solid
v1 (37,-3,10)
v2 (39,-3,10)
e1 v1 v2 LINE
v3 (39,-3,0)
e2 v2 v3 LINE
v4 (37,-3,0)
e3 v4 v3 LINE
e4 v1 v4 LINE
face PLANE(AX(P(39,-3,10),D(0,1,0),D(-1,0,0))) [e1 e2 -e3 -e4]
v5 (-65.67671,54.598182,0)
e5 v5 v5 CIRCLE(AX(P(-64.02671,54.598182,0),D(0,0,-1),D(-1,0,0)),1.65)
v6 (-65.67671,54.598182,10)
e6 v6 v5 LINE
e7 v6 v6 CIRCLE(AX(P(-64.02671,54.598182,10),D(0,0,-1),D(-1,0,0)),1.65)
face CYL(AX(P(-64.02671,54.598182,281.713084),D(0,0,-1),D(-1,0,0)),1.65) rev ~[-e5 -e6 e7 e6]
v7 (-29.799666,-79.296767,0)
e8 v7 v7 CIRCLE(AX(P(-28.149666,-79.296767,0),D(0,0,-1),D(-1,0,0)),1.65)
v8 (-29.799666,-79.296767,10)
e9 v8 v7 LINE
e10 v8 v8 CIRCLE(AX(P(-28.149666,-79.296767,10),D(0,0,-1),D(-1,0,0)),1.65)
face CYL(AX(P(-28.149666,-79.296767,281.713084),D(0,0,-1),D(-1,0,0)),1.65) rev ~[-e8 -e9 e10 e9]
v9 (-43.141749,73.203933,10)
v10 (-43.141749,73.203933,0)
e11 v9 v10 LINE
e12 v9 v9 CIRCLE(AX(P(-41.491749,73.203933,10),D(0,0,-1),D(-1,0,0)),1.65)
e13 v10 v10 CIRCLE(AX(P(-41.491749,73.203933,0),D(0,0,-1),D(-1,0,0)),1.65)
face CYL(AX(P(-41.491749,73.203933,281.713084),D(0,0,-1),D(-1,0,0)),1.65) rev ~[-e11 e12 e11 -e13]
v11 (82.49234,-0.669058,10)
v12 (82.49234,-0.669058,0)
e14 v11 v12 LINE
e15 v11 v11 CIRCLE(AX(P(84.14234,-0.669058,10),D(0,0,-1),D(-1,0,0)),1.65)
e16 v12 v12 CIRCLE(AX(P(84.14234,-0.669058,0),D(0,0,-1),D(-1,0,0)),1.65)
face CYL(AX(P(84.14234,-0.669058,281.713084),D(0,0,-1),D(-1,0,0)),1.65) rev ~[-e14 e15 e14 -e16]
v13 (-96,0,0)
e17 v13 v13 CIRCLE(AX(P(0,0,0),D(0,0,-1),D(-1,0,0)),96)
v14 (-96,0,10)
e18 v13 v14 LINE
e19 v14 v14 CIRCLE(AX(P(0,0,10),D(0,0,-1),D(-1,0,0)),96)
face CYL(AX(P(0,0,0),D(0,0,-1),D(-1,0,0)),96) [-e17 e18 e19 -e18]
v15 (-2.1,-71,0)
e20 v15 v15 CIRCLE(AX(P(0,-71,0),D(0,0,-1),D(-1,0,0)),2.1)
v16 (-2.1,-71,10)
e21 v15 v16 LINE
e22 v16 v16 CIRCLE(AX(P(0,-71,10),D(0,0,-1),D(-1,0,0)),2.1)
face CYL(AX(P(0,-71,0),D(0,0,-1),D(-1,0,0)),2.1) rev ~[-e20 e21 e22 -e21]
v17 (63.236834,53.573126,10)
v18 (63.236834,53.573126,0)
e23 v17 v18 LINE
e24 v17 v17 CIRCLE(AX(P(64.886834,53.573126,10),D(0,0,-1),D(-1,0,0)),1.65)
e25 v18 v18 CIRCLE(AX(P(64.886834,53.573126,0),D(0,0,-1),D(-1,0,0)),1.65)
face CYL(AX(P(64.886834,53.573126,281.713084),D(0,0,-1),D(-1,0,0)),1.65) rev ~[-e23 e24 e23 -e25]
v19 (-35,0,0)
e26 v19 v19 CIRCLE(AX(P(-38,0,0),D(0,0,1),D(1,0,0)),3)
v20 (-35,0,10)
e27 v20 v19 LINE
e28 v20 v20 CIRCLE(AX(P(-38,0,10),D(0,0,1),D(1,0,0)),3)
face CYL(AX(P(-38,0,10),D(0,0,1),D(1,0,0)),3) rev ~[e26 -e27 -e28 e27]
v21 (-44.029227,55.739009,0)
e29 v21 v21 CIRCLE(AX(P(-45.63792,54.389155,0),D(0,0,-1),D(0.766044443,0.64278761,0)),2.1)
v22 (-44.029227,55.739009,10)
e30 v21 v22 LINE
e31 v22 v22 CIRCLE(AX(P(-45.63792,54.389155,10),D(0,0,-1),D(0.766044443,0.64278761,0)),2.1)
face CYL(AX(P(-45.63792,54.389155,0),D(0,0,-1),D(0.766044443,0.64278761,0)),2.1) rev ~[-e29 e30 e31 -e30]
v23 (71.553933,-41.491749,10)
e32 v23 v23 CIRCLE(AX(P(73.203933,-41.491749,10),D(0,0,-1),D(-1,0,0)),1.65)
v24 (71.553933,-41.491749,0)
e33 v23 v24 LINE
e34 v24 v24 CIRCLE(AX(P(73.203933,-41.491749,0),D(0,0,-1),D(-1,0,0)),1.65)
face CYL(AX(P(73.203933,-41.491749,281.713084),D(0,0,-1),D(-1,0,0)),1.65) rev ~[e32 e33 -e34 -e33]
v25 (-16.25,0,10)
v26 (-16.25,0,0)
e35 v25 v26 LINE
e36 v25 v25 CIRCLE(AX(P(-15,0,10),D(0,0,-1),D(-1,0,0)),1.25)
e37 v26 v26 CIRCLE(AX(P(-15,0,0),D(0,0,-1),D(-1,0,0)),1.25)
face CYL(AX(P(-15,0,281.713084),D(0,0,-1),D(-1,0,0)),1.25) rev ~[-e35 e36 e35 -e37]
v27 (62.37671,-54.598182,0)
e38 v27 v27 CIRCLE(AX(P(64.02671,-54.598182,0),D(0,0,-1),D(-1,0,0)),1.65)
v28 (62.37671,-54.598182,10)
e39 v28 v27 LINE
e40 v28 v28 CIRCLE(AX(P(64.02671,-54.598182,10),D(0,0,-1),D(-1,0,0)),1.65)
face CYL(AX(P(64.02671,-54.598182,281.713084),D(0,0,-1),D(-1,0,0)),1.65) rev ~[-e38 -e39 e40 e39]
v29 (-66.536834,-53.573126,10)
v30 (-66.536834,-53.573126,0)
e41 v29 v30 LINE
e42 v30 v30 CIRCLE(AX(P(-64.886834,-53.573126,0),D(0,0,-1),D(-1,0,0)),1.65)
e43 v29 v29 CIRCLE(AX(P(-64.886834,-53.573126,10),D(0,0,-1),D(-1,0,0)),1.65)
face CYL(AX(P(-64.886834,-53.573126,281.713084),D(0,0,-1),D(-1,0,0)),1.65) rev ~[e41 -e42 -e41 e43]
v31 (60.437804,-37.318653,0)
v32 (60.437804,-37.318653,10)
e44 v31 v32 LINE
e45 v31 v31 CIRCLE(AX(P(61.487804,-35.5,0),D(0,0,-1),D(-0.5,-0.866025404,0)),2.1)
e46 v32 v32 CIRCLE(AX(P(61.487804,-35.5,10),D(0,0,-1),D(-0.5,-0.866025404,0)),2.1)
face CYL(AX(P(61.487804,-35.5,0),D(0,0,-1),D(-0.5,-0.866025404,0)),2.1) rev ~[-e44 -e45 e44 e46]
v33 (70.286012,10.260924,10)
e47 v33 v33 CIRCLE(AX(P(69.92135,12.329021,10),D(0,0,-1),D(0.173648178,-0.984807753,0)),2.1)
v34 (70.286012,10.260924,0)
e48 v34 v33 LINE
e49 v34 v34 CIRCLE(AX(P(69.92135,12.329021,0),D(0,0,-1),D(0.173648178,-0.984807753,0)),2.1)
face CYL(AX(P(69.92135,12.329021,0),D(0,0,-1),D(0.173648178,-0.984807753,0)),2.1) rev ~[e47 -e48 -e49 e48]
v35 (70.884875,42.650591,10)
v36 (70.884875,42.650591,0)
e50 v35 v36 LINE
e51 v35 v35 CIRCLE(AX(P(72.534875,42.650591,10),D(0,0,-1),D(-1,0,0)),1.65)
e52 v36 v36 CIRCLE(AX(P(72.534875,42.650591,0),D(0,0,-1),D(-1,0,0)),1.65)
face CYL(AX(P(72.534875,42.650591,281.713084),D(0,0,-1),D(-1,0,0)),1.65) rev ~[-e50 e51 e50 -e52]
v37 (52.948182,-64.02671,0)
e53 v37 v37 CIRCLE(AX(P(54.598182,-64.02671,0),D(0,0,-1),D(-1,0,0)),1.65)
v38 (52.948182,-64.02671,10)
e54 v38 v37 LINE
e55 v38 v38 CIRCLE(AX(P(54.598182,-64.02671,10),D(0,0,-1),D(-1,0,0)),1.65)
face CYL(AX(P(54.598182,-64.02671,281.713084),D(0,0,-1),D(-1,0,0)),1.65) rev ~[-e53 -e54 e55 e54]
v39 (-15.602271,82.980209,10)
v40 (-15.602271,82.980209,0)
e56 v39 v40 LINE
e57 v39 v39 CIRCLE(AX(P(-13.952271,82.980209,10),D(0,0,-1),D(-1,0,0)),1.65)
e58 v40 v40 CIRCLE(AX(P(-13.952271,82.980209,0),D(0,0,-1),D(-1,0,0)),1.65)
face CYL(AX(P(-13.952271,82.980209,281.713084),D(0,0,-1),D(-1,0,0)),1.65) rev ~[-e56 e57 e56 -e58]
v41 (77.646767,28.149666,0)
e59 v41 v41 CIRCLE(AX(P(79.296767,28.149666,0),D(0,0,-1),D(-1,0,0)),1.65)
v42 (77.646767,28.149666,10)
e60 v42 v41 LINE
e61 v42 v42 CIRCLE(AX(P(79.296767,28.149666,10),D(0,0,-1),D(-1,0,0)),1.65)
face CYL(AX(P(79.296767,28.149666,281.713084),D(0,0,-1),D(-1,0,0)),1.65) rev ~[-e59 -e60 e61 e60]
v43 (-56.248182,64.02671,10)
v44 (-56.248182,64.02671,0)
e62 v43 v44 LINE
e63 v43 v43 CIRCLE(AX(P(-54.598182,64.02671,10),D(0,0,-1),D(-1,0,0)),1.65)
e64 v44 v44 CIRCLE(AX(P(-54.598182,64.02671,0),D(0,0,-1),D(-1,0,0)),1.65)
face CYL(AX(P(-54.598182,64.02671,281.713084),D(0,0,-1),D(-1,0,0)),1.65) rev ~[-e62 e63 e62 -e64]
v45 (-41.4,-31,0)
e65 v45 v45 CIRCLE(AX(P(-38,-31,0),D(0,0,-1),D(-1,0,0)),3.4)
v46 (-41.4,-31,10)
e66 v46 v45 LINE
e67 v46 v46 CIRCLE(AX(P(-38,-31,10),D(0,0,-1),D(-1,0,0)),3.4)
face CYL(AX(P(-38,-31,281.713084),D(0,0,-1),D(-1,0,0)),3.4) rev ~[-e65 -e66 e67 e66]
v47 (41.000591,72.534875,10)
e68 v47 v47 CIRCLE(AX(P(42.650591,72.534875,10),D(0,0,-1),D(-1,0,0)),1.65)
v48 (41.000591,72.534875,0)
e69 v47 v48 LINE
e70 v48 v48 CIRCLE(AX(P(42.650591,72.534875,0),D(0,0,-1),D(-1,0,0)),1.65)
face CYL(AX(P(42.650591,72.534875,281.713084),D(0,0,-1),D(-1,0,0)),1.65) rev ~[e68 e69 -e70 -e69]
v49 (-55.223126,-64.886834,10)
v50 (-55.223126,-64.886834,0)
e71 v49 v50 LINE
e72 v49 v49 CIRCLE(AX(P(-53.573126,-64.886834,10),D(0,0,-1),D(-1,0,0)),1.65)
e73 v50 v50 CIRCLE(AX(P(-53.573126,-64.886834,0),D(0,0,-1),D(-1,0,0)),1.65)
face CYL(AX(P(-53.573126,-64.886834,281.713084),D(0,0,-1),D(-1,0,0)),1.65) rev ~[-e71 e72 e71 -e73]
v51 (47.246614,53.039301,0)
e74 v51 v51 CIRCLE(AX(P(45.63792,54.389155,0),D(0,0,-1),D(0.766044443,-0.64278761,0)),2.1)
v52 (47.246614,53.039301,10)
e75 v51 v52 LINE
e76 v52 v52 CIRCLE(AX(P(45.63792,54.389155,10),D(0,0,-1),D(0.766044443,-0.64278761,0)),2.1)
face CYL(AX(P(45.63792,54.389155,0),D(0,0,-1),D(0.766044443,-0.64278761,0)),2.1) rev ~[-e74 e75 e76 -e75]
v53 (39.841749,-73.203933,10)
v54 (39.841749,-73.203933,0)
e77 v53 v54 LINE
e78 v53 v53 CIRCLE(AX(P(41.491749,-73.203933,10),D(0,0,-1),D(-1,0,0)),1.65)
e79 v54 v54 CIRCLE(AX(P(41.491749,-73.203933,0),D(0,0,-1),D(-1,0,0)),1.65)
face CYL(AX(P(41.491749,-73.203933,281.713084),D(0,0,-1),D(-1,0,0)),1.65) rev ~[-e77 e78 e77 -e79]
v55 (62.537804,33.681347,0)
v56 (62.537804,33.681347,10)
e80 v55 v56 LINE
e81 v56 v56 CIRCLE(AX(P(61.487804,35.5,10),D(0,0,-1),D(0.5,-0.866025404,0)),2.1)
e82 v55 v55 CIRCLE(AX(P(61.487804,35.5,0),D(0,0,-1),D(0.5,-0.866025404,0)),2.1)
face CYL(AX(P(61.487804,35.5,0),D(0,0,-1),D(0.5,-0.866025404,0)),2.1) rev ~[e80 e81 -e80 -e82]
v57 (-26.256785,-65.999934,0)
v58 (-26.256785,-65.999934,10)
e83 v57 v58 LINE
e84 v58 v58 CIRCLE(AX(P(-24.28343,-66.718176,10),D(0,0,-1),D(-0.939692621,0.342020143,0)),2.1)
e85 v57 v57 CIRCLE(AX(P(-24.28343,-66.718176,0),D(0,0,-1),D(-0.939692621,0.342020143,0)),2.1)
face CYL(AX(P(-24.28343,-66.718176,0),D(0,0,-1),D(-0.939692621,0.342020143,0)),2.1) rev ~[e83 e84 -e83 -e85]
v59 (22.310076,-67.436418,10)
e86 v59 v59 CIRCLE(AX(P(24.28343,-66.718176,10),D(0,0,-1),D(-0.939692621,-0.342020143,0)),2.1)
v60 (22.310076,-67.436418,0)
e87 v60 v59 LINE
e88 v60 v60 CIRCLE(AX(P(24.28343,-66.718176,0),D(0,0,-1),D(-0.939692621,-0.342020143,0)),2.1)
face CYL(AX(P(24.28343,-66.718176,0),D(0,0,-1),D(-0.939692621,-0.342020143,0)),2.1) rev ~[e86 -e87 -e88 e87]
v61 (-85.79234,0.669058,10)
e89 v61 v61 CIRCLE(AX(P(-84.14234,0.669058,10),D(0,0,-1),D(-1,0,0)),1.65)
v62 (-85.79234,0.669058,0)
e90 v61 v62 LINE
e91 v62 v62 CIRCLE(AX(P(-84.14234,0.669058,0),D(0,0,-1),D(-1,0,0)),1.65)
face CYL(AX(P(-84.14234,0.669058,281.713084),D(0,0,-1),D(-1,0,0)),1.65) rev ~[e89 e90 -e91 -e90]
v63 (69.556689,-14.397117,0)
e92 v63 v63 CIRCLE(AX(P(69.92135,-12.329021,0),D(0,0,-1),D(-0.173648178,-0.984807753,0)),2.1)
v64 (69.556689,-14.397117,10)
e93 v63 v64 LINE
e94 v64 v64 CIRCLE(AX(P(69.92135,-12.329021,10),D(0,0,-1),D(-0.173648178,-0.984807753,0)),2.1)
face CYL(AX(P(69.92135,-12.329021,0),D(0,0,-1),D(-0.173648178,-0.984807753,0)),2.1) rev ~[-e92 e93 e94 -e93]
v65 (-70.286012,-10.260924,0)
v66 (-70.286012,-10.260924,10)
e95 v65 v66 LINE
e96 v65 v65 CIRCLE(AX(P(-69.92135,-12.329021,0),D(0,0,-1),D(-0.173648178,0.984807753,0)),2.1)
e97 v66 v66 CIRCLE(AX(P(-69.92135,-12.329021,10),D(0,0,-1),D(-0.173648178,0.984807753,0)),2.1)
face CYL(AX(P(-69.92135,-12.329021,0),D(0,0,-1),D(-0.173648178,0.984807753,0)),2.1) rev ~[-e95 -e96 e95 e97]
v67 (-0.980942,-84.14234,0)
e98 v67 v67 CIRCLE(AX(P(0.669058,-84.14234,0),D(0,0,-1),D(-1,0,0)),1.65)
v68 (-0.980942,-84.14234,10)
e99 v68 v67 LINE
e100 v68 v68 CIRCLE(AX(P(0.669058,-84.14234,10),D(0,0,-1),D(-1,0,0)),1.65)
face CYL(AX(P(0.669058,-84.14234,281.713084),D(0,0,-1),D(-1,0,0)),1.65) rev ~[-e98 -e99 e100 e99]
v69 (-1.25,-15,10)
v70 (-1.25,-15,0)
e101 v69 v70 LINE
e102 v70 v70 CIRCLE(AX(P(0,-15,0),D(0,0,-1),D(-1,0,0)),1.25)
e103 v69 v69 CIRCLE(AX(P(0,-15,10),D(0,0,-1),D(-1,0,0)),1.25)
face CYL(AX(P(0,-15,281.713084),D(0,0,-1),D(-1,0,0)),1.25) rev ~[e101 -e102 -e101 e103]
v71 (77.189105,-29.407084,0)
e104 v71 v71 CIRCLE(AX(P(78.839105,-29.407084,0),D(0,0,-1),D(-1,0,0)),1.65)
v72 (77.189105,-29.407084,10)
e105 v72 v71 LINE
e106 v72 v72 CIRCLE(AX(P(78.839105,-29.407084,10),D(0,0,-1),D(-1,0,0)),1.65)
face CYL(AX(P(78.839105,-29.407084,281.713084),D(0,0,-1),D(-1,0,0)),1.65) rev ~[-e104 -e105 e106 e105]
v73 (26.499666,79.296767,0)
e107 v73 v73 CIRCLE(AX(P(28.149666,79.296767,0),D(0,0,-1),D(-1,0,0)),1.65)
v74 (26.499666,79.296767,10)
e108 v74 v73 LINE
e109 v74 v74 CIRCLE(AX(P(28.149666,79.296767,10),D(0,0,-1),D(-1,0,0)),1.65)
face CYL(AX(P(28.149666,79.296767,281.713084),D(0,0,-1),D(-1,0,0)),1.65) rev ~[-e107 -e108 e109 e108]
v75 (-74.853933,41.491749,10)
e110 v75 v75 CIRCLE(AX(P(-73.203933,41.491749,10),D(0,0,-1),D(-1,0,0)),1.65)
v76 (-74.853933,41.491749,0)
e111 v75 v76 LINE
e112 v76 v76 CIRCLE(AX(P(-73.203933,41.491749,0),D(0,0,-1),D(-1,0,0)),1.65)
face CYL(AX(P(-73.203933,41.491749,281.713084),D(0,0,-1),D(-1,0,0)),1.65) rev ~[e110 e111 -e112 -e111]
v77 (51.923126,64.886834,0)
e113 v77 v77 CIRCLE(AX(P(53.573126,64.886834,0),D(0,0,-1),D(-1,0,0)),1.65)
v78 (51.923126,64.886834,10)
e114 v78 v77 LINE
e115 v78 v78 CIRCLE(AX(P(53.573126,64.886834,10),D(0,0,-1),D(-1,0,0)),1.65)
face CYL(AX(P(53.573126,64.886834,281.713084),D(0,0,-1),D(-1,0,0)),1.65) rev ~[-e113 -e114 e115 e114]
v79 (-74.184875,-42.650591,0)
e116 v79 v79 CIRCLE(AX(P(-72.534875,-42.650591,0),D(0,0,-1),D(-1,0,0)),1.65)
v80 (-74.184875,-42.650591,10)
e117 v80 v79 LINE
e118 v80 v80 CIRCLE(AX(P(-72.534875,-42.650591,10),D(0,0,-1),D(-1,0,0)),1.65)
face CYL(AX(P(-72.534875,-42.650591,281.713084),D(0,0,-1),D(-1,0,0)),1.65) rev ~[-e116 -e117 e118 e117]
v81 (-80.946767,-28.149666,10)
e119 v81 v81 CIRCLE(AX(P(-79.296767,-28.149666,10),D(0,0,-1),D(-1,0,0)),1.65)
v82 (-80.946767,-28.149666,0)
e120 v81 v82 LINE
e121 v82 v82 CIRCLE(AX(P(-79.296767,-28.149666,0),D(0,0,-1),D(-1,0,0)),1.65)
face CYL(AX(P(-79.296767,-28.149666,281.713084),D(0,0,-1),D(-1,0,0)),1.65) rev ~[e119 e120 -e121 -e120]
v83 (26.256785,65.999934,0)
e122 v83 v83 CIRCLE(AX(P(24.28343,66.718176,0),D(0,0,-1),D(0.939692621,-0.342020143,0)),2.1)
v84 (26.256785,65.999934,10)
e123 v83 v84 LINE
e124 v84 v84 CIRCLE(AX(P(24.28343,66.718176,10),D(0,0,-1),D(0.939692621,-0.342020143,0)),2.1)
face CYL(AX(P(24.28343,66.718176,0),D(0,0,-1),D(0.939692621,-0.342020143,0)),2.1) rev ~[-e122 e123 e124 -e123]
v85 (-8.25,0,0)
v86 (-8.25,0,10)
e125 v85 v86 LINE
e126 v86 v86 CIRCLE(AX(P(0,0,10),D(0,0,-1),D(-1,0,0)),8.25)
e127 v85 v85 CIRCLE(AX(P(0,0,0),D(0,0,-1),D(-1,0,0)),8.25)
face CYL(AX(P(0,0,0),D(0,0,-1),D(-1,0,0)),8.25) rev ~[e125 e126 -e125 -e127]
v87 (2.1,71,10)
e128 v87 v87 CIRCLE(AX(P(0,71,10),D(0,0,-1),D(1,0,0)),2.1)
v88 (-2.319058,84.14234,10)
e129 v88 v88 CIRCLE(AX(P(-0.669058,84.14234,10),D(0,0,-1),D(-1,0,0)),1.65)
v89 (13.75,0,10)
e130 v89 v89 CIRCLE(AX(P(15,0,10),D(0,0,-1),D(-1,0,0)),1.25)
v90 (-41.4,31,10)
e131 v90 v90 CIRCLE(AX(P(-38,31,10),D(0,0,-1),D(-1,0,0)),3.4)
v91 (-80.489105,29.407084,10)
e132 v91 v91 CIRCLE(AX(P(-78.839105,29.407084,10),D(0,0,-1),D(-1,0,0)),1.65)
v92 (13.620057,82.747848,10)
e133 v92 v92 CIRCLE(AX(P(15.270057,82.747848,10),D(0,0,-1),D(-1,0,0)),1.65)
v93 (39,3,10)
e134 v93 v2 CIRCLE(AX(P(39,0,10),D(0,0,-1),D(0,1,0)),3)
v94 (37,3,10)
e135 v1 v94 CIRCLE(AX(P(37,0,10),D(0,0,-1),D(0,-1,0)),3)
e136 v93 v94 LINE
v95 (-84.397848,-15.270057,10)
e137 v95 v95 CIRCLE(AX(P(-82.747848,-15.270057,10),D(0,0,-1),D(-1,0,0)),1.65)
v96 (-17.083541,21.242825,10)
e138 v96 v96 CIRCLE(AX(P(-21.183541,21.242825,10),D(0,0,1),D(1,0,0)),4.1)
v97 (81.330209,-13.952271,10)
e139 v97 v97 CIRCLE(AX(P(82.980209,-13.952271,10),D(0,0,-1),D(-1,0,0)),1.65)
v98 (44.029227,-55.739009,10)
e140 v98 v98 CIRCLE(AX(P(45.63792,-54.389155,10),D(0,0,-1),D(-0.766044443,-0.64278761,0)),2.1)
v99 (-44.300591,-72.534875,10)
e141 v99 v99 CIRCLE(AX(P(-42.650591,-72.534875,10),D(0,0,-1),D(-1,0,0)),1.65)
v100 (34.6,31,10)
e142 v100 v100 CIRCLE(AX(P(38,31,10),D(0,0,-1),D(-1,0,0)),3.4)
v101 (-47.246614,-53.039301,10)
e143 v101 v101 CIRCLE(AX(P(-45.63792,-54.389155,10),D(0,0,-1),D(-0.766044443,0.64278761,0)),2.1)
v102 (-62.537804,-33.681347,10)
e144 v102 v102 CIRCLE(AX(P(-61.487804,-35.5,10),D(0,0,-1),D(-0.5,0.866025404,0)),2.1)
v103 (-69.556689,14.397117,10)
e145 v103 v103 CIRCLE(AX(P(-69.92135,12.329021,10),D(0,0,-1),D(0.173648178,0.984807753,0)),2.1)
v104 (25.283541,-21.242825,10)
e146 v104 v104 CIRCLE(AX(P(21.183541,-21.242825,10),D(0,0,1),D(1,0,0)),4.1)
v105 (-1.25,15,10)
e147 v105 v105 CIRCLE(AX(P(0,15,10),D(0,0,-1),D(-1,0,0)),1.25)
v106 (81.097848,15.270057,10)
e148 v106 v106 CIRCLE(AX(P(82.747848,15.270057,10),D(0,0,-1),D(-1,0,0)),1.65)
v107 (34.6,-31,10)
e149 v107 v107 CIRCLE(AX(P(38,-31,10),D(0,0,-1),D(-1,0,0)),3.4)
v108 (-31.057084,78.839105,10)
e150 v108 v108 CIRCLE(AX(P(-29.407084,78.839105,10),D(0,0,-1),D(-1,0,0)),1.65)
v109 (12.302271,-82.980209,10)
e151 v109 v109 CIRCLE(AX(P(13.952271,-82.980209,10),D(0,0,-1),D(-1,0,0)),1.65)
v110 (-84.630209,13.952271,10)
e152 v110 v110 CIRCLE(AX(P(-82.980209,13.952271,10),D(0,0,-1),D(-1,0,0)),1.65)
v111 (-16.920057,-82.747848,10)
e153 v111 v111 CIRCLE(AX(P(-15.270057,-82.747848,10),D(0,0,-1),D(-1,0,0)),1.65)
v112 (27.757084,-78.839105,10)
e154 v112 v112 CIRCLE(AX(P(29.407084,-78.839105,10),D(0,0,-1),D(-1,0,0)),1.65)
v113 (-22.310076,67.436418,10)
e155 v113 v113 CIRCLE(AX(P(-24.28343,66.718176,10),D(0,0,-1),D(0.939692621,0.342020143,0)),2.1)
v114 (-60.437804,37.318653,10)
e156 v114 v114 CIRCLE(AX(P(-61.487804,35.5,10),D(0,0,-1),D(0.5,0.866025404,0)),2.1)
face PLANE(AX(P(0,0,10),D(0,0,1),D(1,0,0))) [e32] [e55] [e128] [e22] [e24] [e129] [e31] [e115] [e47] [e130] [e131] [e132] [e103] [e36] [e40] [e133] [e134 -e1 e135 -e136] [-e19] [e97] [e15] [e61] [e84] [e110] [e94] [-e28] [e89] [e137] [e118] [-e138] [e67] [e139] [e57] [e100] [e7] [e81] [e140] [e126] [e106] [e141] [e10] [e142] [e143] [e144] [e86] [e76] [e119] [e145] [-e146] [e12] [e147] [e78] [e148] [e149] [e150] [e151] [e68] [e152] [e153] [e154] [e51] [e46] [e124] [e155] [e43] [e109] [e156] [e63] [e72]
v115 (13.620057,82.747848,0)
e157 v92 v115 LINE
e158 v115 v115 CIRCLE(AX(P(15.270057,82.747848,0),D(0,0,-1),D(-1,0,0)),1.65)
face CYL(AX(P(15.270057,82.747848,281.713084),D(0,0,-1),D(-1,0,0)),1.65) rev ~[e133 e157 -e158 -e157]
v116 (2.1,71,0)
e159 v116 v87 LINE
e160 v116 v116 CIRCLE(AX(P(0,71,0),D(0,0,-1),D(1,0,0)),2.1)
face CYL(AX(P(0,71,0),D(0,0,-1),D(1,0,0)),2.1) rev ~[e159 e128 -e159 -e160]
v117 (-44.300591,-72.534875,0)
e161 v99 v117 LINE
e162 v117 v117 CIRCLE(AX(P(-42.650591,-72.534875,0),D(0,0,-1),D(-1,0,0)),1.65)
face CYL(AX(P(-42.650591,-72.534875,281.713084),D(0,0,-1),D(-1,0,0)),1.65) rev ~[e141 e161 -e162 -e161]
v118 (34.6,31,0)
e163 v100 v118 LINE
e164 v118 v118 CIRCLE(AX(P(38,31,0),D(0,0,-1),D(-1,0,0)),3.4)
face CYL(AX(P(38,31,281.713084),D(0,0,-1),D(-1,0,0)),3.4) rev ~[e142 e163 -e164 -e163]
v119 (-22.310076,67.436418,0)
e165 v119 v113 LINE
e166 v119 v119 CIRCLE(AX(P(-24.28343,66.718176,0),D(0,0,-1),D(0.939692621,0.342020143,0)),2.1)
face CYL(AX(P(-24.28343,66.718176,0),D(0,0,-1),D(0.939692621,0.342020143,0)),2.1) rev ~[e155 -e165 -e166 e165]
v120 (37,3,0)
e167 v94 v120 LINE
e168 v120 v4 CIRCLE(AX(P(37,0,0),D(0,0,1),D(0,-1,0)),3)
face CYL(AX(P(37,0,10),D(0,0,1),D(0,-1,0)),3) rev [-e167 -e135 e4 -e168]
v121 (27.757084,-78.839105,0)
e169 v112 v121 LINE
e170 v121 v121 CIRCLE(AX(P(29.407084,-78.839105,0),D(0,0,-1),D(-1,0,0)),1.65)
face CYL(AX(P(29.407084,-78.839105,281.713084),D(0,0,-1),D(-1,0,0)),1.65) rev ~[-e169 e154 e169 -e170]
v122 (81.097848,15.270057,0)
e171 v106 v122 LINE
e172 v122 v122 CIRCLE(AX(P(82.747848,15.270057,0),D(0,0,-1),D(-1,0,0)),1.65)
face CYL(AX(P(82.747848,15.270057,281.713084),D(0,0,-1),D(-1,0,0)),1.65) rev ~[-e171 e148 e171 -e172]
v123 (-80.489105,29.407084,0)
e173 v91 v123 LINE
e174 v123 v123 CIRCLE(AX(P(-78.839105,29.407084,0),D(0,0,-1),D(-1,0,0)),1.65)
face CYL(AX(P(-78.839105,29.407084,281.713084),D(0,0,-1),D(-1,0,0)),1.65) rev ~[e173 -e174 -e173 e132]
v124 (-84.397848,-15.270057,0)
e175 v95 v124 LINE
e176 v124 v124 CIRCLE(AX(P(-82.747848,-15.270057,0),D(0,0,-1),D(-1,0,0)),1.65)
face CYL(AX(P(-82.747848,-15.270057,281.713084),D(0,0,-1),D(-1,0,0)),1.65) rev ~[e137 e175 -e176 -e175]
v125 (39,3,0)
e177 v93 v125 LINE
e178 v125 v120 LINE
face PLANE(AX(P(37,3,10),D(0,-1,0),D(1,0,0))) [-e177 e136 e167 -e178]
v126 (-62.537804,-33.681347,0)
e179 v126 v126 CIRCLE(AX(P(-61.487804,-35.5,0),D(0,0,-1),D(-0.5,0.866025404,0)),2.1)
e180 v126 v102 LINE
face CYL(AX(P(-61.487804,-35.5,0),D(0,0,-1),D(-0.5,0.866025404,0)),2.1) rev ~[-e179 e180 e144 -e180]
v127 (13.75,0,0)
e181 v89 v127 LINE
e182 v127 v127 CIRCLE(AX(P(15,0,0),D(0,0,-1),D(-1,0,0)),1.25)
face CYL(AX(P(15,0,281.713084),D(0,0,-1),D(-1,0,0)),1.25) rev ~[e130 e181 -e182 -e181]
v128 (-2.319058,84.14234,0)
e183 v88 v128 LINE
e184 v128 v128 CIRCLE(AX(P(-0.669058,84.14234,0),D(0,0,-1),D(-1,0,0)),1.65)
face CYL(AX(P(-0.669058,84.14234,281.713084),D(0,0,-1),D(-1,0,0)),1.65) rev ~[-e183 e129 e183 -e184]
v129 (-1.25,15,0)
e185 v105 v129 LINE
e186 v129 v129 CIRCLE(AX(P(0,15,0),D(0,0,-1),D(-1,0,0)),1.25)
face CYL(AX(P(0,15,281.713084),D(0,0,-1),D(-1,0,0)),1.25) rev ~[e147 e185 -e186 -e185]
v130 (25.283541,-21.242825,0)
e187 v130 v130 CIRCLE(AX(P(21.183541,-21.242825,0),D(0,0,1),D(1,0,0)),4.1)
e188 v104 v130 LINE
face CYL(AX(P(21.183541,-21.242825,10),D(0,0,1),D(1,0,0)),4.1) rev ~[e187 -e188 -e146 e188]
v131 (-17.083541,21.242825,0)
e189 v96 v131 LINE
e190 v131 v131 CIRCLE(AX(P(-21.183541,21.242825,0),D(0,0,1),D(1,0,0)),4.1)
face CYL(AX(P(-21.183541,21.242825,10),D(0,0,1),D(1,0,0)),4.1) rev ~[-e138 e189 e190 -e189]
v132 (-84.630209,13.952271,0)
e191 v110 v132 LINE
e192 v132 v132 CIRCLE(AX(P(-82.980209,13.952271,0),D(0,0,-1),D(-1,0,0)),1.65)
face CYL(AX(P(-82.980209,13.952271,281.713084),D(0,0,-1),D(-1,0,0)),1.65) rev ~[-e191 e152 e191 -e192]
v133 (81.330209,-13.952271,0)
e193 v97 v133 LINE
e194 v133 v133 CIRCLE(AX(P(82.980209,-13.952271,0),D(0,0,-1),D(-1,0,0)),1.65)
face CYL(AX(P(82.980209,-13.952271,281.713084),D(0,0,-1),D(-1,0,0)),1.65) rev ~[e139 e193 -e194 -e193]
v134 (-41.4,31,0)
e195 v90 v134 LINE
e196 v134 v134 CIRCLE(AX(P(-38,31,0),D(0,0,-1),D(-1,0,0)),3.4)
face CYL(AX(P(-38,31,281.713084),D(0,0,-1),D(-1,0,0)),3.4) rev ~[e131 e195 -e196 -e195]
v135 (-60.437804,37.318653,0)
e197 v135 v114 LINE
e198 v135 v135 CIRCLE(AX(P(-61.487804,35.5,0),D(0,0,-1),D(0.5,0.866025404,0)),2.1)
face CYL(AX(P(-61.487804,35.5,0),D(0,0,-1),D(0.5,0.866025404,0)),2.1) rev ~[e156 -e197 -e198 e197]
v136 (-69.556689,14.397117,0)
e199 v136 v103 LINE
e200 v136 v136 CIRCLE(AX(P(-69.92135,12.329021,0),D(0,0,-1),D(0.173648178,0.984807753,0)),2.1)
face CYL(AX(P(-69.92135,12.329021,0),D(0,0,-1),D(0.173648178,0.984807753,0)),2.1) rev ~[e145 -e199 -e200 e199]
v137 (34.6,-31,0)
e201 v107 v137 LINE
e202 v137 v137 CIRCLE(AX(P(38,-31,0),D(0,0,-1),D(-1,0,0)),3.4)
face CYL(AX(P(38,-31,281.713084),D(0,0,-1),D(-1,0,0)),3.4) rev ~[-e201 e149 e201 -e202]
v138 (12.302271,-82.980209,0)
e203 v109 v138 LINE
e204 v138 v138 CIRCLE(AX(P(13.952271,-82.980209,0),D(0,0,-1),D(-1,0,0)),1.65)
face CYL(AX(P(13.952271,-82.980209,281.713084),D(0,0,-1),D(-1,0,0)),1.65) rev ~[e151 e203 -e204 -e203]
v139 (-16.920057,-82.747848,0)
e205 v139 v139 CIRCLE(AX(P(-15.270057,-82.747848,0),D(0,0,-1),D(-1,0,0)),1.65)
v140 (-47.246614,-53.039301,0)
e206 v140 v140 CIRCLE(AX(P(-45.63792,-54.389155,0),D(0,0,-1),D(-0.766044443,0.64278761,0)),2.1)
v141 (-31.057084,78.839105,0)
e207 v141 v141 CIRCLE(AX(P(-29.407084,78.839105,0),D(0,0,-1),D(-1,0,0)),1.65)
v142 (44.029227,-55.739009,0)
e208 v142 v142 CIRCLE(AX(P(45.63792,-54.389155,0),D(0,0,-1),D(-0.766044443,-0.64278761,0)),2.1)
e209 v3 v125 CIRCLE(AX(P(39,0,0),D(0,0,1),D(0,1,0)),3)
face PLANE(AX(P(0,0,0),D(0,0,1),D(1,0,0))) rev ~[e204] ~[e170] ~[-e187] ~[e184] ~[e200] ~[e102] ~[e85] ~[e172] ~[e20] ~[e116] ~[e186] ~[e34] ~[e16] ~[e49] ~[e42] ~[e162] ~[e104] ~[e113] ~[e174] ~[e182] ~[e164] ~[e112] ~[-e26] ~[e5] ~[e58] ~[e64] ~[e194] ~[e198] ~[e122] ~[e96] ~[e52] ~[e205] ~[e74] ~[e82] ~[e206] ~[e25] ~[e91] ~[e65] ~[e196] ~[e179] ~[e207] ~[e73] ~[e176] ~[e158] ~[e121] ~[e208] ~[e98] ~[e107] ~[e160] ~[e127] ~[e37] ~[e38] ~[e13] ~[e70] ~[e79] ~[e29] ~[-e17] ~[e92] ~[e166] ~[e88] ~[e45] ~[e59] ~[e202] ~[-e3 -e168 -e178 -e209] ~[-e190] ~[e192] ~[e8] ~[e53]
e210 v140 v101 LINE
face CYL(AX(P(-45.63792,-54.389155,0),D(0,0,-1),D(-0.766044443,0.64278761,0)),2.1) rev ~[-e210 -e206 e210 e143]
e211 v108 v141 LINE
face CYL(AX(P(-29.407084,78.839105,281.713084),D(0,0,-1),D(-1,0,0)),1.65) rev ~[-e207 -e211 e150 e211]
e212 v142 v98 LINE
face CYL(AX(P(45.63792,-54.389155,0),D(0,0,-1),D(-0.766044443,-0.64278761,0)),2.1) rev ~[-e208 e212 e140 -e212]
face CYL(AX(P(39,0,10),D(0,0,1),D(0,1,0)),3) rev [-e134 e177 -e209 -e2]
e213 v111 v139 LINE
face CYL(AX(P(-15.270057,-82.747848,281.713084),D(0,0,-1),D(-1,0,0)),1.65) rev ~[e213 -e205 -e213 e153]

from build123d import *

# Parameters (mm, degrees)
SKETCH1_R           = 102.5
BOSS_EXTRUDE1_DEPTH = 10
SKETCH2_R           = 8.25
CUT_EXTRUDE1_DEPTH  = 146.301410867
SKETCH4_R           = 1
CUT_EXTRUDE3_DEPTH  = 20
CIRPATTERN2_COUNT   = 18
SKETCH5_R           = 2.1
CUT_EXTRUDE4_DEPTH  = 146.301410867
CIRPATTERN3_COUNT   = 18
SKETCH7_R           = 102.5
SKETCH7_R_2         = 96
CUT_EXTRUDE5_DEPTH  = 34
M4_TAPPED_HOLE1_D   = 3.3
M8_TAPPED_HOLE2_D   = 6.8
M3_TAPPED_HOLE1_D   = 2.5
SKETCH44_R          = 4.1
CUT_EXTRUDE19_DEPTH = 10
SKETCH45_R          = 3
CUT_EXTRUDE20_DEPTH = 10
CUT_EXTRUDE21_DEPTH = 137.132288602


with BuildPart() as part:
    # Sketch1 → Boss-Extrude1 (new body)
    with BuildSketch(Plane.XY):
        Circle(SKETCH1_R)
    extrude(amount=BOSS_EXTRUDE1_DEPTH)

    # Sketch2 → Cut-Extrude1 (cut, through all)
    with BuildSketch(Plane(origin=(0, 0, 0), x_dir=(-1, 0, 0), z_dir=(0, 0, -1))):
        Circle(SKETCH2_R)
    extrude(amount=-CUT_EXTRUDE1_DEPTH, mode=Mode.SUBTRACT)

    # Sketch4 → Cut-Extrude3 (cut)
    with BuildSketch(Plane(origin=(0, 0, 0), x_dir=(-1, 0, 0), z_dir=(0, 0, -1))):
        with Locations((-29.407083899, -78.839104774)):
            Circle(SKETCH4_R)
        with Locations(Location((-13.952270679, -82.980209495, 0), (0, 0, 180))):
            Circle(SKETCH4_R)
    cut_extrude3 = extrude(amount=-CUT_EXTRUDE3_DEPTH, mode=Mode.SUBTRACT)

    # CirPattern2: Cut-Extrude3 ×18 about axis
    cirpattern2_axis = Axis((0, 0, 0), (0, 0, 1))
    for i in range(1, CIRPATTERN2_COUNT):
        add(cut_extrude3.rotate(cirpattern2_axis, i * 360 / CIRPATTERN2_COUNT), mode=Mode.SUBTRACT)

    # Sketch5 → Cut-Extrude4 (cut, through all)
    with BuildSketch(Plane(origin=(0, 0, 0), x_dir=(-1, 0, 0), z_dir=(0, 0, -1))):
        with Locations((0, -71)):
            Circle(SKETCH5_R)
    cut_extrude4 = extrude(amount=-CUT_EXTRUDE4_DEPTH, mode=Mode.SUBTRACT)

    # CirPattern3: Cut-Extrude4 ×18 about axis
    cirpattern3_axis = Axis((0, 0, 0), (0, 0, 1))
    for i in range(1, CIRPATTERN3_COUNT):
        add(cut_extrude4.rotate(cirpattern3_axis, i * 360 / CIRPATTERN3_COUNT), mode=Mode.SUBTRACT)

    # Sketch7 → Cut-Extrude5 (cut)
    with BuildSketch(Plane(origin=(0, 0, 0), x_dir=(-1, 0, 0), z_dir=(0, 0, -1))):
        Circle(SKETCH7_R)
        Circle(SKETCH7_R_2, mode=Mode.SUBTRACT)
    extrude(amount=-CUT_EXTRUDE5_DEPTH, mode=Mode.SUBTRACT)

    # M4 Tapped Hole1 (through all)
    with Locations(Plane(origin=(-15.270057345, -82.747848151, 10), x_dir=(1, 0, 0), z_dir=(0, 0, 1))):
        with Locations((0, 0), (-12.879609153, 3.451080871), (-27.380533745, 10.212973059), (-38.303068251, 17.861014056), (-49.61677675, 29.174722555), (-57.264817747, 40.097257061), (-64.026709935, 54.598181653), (-67.477790806, 67.477790806), (-68.87228269, 83.416905976), (-67.71015215, 96.70011883), (-63.569047429, 112.15493205), (-57.933875572, 124.239597096), (-48.75665259, 137.346029805), (-39.328124309, 146.774558086), (-26.2216916, 155.951781068), (-14.137026554, 161.586952925), (1.317786666, 165.728057646), (14.60099952, 166.890188186), (30.54011469, 165.495696302), (43.419723843, 162.044615431), (57.920648435, 155.282723243), (68.843182941, 147.634682246), (80.15689144, 136.320973747), (87.804932437, 125.398439241), (94.566824625, 110.897514649), (98.017905496, 98.017905496), (99.41239738, 82.078790326), (98.25026684, 68.795577472), (94.109162119, 53.340764252), (88.473990262, 41.256099206), (79.29676728, 28.149666497), (69.868238999, 18.721138216), (56.76180629, 9.543915234), (44.677141244, 3.908743377), (29.222328024, -0.232361344), (15.93911517, -1.394491884)):
            Hole(M4_TAPPED_HOLE1_D / 2)

    # M8 Tapped Hole2 (through all)
    with Locations(Plane.XY.offset(10)):
        with Locations((-38, 31), (-38, -31), (38, 31), (38, -31)):
            Hole(M8_TAPPED_HOLE2_D / 2)

    # M3 Tapped Hole1 (through all)
    with Locations(Plane(origin=(0, 15, 10), x_dir=(1, 0, 0), z_dir=(0, 0, 1))):
        with Locations((0, 0), (15, -15), (0, -30), (-15, -15)):
            Hole(M3_TAPPED_HOLE1_D / 2)

    # Sketch44 → Cut-Extrude19 (cut)
    with BuildSketch(Plane.XY.offset(10)):
        with Locations((21.183540931, -21.242824521)):
            Circle(SKETCH44_R)
        with Locations((-21.183540931, 21.242824521)):
            Circle(SKETCH44_R)
    extrude(amount=-CUT_EXTRUDE19_DEPTH, mode=Mode.SUBTRACT)

    # Sketch45 → Cut-Extrude20 (cut)
    with BuildSketch(Plane.XY.offset(10)):
        with Locations((-38, 0)):
            Circle(SKETCH45_R)
        with Locations((38, 0)):
            Circle(SKETCH45_R)
    extrude(amount=-CUT_EXTRUDE20_DEPTH, mode=Mode.SUBTRACT)

    # Sketch47 → Cut-Extrude21 (cut, through all)
    with BuildSketch(Plane.XY.offset(10)):
        with BuildLine():
            Line((37, 3), (39, 3))
            ThreePointArc((39, 3), (42, 0), (39, -3))
            Line((39, -3), (37, -3))
            ThreePointArc((37, -3), (34, 0), (37, 3))
        make_face()
    extrude(amount=-CUT_EXTRUDE21_DEPTH, mode=Mode.SUBTRACT)


solid = part.part
